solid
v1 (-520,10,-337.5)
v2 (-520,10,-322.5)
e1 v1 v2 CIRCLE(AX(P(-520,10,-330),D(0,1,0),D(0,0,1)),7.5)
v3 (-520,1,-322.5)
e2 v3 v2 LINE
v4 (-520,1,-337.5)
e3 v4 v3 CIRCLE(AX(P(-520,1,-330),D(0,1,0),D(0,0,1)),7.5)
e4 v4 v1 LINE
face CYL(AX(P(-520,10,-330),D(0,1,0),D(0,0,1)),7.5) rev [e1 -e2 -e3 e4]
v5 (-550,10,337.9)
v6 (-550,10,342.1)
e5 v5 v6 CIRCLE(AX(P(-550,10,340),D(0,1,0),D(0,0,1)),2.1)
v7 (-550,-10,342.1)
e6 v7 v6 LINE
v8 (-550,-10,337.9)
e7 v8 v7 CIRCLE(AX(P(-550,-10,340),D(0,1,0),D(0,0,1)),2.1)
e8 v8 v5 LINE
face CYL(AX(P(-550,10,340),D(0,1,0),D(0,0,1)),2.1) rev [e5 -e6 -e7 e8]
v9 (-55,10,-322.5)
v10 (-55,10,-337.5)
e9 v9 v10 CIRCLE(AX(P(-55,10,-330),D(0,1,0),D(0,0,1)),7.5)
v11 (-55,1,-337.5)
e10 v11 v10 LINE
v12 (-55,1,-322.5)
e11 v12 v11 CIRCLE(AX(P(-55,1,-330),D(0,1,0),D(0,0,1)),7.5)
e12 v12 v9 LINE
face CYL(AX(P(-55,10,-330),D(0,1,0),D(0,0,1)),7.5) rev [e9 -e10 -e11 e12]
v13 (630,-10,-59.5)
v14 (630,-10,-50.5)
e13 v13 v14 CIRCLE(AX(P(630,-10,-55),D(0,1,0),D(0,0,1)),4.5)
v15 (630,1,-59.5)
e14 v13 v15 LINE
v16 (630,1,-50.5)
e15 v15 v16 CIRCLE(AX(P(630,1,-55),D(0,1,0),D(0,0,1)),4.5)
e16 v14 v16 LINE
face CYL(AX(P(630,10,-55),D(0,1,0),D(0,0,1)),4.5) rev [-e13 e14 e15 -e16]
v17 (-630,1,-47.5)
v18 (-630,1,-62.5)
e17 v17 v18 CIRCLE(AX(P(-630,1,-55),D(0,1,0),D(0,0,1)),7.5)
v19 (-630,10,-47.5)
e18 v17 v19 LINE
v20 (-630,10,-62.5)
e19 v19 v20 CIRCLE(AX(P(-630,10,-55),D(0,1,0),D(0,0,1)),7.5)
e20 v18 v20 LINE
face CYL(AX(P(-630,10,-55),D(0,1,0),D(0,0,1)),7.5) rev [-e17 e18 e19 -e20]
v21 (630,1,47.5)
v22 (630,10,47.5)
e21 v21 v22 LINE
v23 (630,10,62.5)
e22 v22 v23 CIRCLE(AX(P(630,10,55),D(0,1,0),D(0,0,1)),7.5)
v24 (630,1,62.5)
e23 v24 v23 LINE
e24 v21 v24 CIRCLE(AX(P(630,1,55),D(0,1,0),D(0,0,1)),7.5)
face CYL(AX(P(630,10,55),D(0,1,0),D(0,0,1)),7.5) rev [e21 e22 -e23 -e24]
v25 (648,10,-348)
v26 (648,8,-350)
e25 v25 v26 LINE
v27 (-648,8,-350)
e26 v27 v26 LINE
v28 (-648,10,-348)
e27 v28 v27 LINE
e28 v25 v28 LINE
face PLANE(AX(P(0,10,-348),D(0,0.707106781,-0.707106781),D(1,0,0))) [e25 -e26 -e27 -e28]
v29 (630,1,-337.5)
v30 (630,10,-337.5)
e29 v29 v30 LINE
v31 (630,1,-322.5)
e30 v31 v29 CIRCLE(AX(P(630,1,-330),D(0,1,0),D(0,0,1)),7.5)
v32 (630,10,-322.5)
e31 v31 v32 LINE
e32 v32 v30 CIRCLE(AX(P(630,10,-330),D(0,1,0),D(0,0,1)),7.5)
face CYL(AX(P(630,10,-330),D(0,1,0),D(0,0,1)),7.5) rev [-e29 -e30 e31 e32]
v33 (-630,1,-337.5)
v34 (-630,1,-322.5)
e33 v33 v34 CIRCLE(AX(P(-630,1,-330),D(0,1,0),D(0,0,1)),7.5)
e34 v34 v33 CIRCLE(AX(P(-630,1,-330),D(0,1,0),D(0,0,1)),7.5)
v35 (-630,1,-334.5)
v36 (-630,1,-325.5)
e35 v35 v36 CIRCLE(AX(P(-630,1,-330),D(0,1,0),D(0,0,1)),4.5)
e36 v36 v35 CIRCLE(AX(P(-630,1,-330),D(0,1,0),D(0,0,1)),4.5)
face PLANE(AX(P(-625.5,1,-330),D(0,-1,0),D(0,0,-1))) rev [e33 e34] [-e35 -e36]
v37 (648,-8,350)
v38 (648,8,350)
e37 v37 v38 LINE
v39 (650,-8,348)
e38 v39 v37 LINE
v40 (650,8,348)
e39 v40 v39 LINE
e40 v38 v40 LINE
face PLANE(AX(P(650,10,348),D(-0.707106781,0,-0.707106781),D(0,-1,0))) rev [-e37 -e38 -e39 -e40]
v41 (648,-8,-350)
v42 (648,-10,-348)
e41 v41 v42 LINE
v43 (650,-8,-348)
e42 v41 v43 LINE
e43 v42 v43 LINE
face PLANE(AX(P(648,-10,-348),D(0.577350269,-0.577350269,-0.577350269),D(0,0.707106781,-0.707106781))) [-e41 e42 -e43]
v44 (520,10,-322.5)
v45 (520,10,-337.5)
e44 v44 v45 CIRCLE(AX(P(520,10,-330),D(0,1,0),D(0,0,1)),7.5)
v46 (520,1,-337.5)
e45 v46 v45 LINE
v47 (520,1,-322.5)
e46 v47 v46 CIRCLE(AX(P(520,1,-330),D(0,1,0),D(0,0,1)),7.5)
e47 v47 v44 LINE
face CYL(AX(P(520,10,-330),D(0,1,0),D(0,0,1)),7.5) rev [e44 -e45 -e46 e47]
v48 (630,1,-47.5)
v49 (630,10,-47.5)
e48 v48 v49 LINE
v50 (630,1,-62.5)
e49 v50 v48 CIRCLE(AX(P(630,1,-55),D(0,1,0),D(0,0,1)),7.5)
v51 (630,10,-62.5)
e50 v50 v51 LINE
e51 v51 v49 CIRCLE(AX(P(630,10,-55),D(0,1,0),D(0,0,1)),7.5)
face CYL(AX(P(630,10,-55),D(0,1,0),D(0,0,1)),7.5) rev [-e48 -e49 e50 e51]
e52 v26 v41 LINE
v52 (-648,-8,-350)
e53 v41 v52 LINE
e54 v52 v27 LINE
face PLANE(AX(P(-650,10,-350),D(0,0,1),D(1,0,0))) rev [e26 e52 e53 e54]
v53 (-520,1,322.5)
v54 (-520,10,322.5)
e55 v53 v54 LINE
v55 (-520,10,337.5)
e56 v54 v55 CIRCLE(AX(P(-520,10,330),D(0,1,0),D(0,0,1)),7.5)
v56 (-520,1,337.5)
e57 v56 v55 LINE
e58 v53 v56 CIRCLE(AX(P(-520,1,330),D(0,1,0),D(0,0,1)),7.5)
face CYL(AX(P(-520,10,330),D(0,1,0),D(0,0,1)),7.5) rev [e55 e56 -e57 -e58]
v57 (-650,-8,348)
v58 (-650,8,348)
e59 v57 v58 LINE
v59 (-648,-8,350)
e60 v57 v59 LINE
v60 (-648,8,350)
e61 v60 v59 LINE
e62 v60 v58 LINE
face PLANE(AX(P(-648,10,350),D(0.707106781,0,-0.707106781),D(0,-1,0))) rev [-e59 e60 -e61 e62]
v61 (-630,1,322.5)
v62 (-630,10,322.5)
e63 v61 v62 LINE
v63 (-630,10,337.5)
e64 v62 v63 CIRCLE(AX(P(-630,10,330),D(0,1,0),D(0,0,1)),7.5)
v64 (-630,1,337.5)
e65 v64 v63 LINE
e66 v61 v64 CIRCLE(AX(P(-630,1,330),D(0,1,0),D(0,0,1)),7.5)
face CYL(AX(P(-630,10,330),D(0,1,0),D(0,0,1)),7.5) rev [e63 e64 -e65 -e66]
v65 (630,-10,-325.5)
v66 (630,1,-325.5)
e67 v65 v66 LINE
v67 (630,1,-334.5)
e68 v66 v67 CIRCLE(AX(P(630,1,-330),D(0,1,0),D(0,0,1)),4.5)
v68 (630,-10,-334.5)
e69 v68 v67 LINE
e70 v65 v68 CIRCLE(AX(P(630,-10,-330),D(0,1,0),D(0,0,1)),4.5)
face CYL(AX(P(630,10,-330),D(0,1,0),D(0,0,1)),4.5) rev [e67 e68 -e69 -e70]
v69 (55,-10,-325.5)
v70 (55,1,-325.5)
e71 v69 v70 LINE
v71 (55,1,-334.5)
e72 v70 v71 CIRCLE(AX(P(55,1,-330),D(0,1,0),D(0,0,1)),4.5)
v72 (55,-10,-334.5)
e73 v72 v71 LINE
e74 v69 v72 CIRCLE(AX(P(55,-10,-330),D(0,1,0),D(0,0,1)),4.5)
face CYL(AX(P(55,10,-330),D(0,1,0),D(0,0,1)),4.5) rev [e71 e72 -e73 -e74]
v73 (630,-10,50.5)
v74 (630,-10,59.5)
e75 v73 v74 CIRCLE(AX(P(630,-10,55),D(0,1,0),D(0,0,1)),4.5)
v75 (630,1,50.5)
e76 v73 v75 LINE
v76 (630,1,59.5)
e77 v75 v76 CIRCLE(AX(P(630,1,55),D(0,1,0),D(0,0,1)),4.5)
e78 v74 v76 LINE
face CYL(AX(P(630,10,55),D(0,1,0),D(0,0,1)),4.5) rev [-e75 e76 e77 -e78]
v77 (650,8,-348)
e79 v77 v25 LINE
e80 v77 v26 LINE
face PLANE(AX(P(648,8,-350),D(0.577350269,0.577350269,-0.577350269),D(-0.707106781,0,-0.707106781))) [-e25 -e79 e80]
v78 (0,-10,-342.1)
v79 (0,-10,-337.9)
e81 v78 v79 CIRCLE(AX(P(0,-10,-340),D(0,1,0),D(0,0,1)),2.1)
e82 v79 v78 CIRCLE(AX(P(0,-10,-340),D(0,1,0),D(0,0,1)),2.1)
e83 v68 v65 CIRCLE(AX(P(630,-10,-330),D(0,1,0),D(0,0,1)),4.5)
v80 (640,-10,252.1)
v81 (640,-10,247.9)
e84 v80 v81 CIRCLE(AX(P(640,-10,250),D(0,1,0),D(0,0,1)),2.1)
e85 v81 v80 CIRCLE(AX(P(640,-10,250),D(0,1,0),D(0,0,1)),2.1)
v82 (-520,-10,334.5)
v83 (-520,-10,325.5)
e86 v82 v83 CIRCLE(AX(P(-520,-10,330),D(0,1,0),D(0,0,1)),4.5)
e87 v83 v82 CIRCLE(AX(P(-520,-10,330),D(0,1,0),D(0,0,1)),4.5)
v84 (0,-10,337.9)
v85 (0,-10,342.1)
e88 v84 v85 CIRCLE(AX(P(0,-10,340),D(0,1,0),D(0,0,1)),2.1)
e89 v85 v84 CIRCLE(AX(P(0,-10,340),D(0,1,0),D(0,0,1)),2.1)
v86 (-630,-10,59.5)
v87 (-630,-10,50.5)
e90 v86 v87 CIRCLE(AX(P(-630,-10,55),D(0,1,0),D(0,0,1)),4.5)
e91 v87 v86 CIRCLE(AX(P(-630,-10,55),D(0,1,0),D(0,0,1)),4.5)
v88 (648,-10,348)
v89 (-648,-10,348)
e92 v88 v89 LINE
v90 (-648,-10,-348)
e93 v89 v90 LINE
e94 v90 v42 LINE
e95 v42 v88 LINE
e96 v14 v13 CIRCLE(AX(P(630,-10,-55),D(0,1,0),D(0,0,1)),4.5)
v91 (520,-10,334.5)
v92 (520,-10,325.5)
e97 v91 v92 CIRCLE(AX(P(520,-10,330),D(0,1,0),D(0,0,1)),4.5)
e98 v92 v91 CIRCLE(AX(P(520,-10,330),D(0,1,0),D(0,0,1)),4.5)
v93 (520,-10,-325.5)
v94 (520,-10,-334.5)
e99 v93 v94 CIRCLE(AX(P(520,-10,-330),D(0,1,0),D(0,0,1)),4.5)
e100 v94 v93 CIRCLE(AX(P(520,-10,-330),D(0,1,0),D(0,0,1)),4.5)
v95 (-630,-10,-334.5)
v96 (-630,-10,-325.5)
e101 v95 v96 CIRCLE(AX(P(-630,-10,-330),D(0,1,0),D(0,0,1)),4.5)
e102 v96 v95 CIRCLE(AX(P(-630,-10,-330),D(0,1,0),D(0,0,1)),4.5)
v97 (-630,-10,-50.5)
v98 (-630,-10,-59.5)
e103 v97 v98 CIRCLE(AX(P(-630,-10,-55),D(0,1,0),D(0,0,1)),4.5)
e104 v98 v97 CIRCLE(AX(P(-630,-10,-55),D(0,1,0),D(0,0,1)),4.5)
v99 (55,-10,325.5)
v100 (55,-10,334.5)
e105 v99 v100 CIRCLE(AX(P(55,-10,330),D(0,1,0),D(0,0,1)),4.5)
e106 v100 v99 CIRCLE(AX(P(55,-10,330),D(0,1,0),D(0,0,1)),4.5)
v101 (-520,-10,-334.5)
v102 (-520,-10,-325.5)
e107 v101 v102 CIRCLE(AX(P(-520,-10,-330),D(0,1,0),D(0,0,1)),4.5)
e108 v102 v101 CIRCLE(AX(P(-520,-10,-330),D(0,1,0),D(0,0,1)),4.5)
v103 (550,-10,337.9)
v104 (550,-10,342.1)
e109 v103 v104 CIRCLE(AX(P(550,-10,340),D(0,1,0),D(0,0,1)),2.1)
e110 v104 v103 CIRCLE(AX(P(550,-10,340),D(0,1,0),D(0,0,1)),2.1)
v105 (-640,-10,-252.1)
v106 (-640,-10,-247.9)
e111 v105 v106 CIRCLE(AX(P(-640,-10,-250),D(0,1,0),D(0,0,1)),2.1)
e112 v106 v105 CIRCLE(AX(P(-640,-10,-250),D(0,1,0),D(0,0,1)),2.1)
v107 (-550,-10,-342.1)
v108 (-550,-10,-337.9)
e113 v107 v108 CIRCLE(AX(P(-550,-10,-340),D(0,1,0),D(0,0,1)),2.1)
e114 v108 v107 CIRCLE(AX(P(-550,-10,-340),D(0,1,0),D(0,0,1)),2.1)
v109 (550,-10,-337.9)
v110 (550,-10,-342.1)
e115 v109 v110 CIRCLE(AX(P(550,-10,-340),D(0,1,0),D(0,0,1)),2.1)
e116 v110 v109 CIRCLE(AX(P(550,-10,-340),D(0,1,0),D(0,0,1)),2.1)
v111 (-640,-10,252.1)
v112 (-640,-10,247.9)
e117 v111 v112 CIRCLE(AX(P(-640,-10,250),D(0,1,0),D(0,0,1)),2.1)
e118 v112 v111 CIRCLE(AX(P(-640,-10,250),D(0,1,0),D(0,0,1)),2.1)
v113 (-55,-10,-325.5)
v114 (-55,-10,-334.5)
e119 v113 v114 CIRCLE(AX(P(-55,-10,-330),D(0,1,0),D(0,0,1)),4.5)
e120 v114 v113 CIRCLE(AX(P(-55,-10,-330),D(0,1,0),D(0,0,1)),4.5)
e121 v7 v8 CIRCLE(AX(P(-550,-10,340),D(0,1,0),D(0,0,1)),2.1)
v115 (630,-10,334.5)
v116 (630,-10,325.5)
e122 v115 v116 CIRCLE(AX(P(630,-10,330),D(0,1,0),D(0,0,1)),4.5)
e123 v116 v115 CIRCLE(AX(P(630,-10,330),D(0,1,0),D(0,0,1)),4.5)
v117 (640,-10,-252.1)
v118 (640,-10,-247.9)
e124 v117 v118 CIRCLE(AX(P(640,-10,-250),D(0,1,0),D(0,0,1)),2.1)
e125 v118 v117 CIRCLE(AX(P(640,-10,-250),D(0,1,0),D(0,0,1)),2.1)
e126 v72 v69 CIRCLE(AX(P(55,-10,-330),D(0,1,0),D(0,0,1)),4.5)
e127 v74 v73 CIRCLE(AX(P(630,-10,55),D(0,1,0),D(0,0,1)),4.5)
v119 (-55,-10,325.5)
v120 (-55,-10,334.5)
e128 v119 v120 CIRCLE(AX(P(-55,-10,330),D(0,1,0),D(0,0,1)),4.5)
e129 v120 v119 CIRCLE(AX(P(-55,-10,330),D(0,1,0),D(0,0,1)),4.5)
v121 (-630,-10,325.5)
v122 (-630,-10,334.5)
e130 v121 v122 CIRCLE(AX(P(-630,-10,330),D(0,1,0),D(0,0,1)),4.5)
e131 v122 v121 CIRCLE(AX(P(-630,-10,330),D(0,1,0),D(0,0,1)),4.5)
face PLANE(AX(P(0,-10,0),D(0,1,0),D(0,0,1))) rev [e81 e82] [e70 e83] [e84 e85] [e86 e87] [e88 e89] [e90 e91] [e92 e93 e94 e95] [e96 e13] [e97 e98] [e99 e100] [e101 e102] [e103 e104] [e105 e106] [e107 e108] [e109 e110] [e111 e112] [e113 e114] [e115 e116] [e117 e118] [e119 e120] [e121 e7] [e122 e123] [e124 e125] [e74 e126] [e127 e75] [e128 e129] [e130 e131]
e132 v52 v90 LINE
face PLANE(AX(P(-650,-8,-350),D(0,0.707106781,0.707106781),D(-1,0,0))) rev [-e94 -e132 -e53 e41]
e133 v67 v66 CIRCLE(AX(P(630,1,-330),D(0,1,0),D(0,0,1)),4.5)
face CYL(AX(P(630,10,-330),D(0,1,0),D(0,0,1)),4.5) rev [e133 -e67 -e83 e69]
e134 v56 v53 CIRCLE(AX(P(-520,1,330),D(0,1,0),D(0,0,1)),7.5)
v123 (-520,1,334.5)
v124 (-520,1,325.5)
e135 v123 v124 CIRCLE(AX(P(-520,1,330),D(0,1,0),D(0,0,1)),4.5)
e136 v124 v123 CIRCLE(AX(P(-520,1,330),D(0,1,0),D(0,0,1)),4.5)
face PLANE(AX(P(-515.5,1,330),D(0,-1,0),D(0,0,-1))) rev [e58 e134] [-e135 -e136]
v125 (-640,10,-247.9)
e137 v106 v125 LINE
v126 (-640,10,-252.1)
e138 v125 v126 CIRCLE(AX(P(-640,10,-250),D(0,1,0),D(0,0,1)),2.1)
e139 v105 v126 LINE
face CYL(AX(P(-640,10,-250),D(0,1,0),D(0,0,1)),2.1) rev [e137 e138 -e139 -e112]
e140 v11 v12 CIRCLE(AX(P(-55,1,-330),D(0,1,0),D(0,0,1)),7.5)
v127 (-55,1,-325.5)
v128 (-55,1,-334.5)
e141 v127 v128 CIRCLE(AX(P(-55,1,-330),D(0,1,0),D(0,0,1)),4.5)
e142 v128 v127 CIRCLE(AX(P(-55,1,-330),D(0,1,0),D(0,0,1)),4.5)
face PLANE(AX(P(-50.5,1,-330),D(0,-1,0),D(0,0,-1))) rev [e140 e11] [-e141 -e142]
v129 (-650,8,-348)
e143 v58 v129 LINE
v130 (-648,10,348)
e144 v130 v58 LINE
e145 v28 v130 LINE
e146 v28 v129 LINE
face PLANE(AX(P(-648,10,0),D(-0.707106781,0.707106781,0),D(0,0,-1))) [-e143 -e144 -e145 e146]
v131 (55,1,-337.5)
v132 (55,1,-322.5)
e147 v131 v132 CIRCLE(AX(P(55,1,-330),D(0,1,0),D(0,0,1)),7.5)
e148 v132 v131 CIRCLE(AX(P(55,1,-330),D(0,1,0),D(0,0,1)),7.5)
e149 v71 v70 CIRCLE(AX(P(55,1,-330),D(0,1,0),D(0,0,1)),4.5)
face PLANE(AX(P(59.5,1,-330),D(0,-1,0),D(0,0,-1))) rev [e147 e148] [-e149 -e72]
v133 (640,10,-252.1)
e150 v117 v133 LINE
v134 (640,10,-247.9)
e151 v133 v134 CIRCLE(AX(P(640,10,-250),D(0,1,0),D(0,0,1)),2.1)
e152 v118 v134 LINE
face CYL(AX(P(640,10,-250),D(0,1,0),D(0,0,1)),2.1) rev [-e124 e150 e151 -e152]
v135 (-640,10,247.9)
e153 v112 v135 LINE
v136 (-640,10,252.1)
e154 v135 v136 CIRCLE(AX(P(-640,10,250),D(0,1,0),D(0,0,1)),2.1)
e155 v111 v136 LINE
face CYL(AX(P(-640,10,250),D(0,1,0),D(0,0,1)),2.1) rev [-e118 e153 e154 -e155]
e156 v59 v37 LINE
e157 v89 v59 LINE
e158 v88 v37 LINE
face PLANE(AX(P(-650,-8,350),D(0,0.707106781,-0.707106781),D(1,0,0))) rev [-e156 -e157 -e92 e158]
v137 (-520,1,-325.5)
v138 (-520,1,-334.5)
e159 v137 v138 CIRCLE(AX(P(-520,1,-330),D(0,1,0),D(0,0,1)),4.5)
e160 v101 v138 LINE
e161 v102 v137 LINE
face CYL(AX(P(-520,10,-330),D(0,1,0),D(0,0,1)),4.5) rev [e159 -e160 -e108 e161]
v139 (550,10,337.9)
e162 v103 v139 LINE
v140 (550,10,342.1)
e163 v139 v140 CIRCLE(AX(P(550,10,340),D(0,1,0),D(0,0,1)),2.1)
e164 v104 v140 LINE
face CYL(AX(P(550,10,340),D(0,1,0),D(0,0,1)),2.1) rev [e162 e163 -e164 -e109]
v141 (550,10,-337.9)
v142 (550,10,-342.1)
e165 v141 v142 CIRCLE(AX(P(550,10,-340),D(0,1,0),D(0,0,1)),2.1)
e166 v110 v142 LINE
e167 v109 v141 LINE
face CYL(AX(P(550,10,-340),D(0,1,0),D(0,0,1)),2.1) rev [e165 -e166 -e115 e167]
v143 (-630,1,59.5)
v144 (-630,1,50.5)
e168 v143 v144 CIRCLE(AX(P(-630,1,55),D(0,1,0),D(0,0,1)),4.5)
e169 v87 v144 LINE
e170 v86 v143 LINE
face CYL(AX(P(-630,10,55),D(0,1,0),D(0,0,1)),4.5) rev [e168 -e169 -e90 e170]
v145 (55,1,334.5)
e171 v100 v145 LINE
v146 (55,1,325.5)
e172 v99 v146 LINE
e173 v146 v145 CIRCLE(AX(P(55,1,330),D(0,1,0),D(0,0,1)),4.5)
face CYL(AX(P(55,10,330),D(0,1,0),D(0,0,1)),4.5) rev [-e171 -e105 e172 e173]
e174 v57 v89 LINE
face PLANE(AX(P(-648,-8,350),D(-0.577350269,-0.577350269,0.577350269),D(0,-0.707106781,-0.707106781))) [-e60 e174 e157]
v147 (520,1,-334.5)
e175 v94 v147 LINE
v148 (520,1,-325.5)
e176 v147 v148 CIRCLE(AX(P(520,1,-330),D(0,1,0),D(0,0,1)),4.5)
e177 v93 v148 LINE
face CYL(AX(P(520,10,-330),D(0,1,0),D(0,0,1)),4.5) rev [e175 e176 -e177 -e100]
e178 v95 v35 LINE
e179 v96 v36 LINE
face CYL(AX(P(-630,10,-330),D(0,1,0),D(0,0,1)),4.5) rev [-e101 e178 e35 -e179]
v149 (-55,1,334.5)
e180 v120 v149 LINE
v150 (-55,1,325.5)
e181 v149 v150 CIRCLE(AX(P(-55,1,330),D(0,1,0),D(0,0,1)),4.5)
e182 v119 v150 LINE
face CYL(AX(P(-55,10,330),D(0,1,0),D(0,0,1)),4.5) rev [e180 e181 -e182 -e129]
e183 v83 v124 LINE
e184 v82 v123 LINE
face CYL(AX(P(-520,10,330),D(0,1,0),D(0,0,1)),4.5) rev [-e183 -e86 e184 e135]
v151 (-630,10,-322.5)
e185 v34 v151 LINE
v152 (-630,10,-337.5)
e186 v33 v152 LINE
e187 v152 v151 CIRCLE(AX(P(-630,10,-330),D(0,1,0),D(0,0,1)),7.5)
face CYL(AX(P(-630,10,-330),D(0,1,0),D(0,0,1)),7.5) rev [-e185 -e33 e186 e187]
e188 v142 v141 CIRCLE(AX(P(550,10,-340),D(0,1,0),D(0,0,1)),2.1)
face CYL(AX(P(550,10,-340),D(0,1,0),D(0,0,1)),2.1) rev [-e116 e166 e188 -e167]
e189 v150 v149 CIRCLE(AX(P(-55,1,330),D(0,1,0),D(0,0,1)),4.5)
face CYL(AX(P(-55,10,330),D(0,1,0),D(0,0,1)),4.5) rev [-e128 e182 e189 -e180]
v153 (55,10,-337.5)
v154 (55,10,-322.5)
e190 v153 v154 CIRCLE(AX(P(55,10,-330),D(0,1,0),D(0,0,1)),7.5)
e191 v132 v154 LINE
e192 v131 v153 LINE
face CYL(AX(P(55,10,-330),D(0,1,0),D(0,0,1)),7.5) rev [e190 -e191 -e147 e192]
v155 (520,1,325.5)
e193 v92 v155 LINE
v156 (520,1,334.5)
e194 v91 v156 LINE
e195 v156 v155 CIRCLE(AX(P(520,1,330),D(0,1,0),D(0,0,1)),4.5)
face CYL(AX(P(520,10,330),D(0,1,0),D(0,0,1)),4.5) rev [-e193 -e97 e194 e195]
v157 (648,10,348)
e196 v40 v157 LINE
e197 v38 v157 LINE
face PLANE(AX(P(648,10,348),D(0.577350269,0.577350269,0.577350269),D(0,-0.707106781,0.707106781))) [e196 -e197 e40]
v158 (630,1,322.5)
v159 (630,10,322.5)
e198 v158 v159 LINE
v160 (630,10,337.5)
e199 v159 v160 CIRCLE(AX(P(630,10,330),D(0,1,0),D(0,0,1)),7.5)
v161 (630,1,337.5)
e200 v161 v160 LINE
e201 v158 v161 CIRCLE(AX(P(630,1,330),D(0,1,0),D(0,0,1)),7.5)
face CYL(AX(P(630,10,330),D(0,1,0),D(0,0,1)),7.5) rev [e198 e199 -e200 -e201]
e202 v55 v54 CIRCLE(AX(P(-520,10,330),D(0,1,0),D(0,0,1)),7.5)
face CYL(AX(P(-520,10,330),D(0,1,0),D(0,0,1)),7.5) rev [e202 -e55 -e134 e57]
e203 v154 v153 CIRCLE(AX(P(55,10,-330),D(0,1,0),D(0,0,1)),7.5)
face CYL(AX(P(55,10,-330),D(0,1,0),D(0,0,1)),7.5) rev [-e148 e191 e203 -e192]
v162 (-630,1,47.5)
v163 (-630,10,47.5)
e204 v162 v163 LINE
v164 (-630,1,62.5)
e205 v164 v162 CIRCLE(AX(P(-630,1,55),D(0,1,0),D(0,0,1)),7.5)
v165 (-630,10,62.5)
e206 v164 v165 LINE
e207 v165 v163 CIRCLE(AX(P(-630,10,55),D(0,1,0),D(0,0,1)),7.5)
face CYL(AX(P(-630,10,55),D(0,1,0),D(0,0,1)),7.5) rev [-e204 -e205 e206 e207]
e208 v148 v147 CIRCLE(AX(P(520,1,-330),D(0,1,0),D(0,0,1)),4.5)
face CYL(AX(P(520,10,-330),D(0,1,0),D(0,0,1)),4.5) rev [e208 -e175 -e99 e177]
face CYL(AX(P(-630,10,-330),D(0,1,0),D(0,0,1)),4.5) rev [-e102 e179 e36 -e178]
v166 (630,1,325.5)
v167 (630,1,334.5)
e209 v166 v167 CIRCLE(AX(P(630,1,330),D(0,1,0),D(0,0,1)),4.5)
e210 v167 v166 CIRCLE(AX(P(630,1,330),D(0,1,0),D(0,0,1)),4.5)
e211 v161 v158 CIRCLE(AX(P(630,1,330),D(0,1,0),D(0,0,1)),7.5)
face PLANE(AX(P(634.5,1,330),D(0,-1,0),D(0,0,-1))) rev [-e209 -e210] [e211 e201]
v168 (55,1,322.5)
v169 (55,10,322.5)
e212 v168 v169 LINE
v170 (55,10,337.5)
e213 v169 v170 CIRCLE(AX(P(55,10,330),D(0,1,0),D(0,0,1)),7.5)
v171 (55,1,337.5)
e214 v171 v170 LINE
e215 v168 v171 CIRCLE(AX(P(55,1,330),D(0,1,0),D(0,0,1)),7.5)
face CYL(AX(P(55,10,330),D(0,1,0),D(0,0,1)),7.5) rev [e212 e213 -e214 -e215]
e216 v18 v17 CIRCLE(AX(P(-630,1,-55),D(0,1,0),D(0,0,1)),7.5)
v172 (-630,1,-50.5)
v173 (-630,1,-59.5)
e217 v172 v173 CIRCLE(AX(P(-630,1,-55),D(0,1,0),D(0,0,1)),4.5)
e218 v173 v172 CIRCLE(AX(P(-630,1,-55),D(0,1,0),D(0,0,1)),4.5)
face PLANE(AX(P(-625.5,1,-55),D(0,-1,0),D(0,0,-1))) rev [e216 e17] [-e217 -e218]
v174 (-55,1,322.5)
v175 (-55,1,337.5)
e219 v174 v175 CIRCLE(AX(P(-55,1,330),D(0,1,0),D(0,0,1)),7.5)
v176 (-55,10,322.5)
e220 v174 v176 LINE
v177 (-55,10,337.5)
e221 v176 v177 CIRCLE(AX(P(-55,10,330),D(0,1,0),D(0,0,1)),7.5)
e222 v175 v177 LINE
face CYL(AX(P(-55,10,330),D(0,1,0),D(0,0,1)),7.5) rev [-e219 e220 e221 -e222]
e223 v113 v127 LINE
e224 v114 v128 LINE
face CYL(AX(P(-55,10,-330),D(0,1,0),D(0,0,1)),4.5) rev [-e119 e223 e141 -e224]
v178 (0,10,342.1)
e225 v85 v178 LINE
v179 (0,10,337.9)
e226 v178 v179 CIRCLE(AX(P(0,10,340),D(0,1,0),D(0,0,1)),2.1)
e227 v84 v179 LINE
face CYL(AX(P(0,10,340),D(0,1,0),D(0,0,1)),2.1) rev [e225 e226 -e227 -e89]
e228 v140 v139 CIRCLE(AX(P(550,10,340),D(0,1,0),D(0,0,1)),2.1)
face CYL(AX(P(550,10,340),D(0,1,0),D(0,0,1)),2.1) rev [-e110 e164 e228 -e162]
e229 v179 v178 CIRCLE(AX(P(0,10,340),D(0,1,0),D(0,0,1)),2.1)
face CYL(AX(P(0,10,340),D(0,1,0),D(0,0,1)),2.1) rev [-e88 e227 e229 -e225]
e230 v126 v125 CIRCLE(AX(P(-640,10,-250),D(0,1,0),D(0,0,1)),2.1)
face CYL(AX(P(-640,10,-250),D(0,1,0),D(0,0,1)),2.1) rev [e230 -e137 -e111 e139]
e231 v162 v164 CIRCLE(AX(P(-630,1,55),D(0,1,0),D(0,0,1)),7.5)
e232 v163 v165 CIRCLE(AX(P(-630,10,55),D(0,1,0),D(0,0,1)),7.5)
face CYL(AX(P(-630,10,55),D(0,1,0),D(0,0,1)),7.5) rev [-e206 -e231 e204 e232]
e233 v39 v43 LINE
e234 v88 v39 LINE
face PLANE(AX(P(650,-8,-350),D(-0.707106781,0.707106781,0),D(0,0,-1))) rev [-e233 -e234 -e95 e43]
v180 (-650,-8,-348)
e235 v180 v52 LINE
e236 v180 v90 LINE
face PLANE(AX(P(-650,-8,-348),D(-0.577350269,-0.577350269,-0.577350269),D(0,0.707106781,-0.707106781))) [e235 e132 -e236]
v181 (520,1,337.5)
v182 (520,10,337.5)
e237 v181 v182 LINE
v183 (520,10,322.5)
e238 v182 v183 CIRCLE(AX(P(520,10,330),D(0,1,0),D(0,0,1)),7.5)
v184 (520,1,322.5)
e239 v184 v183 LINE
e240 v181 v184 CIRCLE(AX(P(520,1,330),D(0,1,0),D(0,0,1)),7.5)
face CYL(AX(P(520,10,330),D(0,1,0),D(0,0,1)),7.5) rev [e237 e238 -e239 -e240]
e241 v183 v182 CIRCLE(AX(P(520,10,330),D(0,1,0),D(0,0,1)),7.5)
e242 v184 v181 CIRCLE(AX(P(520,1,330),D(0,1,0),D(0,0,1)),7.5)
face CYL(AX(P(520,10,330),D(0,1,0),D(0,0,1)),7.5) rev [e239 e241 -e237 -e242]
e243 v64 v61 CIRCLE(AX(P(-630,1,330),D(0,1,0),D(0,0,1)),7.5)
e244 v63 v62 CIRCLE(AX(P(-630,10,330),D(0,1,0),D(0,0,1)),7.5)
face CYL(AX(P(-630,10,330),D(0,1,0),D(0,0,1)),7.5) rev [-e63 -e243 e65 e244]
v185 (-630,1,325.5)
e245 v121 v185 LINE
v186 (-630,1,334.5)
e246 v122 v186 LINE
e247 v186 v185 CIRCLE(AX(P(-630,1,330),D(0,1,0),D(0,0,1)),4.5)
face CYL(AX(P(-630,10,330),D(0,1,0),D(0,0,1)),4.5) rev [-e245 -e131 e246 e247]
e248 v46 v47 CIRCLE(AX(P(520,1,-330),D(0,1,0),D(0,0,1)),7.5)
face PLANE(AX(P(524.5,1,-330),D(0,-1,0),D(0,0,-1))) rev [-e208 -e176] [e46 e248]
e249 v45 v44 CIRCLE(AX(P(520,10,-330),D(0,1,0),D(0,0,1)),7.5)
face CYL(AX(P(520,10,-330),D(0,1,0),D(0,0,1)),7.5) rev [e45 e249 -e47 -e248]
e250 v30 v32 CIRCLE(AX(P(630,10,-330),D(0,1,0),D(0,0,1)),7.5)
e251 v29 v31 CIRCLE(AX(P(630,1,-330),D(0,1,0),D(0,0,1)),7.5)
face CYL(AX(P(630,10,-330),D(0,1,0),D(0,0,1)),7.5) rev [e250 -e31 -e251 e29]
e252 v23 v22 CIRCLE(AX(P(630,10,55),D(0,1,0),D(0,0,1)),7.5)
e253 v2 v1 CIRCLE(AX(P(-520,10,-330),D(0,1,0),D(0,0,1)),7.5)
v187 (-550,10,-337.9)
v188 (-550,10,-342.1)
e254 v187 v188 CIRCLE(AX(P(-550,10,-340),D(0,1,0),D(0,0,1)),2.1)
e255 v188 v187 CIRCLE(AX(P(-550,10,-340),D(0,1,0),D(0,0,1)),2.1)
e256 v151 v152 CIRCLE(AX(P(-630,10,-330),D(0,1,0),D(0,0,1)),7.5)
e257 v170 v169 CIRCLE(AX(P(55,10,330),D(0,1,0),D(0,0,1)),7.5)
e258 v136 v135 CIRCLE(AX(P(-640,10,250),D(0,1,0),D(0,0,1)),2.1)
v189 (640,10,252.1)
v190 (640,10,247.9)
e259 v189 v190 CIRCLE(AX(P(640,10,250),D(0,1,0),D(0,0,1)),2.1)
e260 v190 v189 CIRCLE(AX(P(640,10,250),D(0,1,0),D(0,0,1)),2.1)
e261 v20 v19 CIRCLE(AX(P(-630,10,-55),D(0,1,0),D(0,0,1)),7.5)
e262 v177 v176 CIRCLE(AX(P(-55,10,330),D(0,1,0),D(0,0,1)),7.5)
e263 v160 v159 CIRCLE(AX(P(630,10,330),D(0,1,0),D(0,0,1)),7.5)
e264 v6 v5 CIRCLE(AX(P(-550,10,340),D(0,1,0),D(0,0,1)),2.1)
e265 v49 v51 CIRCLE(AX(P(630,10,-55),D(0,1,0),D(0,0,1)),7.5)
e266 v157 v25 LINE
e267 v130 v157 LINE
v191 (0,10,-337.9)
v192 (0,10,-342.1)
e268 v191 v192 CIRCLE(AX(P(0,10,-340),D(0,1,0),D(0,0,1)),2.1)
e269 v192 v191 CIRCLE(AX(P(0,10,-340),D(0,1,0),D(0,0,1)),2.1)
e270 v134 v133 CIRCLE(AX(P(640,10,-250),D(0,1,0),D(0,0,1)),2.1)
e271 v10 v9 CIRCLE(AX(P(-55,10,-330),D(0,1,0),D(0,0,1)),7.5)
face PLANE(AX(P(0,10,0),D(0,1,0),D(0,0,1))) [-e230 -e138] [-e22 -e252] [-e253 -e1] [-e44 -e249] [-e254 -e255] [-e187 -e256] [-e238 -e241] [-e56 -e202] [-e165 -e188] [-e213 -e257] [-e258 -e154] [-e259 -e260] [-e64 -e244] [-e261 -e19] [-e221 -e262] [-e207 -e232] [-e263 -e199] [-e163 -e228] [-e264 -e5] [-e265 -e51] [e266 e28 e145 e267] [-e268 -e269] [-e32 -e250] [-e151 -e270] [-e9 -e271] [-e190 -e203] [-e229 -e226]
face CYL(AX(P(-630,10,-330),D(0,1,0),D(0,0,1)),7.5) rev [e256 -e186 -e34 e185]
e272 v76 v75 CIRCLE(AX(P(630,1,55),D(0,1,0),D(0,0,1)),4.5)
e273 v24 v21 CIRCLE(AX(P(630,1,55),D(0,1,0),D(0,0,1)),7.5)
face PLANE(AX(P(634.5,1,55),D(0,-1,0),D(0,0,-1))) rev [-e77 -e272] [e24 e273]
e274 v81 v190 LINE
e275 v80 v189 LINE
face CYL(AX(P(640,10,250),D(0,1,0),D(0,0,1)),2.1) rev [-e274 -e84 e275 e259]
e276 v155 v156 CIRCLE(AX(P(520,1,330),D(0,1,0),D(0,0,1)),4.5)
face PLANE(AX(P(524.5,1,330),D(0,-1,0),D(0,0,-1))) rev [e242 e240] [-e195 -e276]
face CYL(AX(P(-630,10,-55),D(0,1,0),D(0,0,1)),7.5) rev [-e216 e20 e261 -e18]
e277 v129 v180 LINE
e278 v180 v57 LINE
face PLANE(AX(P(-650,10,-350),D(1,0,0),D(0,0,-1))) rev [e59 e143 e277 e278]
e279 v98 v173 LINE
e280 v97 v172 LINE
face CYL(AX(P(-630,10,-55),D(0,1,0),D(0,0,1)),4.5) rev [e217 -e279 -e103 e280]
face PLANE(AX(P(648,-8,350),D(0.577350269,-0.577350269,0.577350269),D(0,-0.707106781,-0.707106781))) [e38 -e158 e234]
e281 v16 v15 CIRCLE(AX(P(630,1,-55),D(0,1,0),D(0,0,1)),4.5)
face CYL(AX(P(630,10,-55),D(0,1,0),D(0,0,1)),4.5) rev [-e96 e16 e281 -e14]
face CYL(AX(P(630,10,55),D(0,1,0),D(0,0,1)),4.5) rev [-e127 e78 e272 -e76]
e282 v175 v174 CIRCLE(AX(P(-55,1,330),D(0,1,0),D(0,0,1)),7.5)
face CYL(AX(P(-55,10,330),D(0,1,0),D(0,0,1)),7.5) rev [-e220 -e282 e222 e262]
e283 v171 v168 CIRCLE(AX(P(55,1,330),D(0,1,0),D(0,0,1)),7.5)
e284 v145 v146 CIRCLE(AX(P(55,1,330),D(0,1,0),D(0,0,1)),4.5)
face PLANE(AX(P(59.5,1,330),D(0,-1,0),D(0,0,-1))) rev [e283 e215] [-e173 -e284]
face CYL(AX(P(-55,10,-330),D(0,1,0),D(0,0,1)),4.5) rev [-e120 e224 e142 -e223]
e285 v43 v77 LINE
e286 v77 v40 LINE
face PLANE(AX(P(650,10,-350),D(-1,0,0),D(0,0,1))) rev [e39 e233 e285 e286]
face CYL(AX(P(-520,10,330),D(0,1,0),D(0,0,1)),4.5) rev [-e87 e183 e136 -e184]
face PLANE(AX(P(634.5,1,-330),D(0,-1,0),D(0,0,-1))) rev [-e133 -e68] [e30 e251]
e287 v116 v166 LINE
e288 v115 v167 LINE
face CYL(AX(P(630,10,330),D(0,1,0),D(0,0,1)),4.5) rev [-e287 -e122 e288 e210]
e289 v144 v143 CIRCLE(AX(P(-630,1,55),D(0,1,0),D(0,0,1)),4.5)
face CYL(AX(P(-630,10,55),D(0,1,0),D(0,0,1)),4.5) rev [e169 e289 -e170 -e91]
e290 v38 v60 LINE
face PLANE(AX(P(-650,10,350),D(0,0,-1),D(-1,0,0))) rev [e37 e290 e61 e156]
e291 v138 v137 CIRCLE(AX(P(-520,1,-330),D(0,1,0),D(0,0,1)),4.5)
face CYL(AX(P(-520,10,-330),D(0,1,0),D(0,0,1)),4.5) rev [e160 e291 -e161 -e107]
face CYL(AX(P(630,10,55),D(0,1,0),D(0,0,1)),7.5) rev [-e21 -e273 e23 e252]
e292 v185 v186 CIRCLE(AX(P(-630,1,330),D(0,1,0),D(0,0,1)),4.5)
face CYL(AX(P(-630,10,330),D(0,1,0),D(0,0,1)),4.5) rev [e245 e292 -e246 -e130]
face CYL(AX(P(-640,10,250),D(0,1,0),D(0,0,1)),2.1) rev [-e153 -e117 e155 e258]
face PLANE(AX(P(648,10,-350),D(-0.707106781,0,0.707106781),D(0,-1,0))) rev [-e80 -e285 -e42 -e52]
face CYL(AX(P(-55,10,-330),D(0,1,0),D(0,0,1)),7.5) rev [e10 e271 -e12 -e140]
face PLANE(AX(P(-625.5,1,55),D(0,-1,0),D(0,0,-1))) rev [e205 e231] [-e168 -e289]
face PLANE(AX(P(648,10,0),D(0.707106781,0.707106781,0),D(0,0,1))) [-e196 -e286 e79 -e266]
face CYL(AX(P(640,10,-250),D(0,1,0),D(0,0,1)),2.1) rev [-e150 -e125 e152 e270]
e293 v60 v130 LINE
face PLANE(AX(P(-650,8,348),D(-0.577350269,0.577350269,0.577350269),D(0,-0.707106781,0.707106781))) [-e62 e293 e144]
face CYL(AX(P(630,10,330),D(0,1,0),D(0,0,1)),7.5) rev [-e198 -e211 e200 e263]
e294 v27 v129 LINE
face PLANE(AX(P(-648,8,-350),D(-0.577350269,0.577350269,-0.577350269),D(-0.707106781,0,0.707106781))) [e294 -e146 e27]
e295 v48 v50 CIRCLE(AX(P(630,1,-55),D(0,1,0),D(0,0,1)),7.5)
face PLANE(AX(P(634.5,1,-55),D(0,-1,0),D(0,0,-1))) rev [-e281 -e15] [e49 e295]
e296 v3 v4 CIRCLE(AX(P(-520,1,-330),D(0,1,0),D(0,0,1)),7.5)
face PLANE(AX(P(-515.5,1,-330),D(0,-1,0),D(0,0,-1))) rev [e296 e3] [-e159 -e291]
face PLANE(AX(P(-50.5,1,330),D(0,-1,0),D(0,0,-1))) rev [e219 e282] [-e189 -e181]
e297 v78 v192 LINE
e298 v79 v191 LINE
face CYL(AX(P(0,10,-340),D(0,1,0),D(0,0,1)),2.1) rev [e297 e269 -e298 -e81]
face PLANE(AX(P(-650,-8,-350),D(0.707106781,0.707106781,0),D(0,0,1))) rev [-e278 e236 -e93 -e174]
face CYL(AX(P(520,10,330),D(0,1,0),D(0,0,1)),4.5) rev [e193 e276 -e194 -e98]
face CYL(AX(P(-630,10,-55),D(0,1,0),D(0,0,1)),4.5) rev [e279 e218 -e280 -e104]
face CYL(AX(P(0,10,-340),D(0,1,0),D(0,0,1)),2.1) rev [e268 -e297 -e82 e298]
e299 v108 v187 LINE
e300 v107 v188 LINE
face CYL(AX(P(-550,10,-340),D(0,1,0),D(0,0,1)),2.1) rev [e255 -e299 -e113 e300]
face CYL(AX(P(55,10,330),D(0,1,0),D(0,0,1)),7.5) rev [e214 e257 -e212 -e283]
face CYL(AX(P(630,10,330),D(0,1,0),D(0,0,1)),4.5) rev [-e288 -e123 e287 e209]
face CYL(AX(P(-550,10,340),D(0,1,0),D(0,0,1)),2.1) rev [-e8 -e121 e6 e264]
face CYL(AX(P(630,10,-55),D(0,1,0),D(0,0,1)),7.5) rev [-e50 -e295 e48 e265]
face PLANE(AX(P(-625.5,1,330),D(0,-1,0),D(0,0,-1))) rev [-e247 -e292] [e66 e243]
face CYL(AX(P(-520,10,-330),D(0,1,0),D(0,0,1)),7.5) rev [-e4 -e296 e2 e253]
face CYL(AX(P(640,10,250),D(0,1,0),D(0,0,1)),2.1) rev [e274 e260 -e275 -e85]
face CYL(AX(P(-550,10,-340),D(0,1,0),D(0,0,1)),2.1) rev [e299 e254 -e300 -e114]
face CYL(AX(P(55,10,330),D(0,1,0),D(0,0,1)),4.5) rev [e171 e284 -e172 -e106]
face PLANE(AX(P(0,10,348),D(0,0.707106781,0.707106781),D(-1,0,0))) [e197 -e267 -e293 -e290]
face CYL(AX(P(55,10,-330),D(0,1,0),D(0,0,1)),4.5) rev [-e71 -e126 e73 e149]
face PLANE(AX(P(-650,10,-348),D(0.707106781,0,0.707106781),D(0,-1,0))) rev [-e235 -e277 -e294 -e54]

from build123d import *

# Parameters (mm, degrees)
SKETCH_1_W                          = 1300
SKETCH_1_H                          = 700
EXTRUDE_1_DEPTH                     = 10
CHAMFER_1_SIZE                      = 2
HOLE_WIZARD_1_D                     = 9
HOLE_WIZARD_1_CBORE_D               = 15
HOLE_WIZARD_1_CBORE_DEPTH           = 9
PATTERN_LINEAR_1_COUNT              = 2
PATTERN_LINEAR_1_PITCH              = 110
HOLE_WIZARD_2_D                     = 9
HOLE_WIZARD_2_CBORE_D               = 15
HOLE_WIZARD_2_CBORE_DEPTH           = 9
PATTERN_LINEAR_2_COUNT              = 2
PATTERN_LINEAR_2_PITCH              = 110
MIRROR_1_COPY_1_D                   = 9
MIRROR_1_COPY_1_CBORE_D             = 15
MIRROR_1_COPY_1_CBORE_DEPTH         = 9
MIRROR_2_COPY_1_D                   = 9
MIRROR_2_COPY_1_CBORE_D             = 15
MIRROR_2_COPY_1_CBORE_DEPTH         = 9
PATTERN_LINEAR_3_COUNT              = 3
PATTERN_LINEAR_3_PITCH              = 575
PATTERN_LINEAR_3_COPY_1_D           = 9
PATTERN_LINEAR_3_COPY_1_CBORE_D     = 15
PATTERN_LINEAR_3_COPY_1_CBORE_DEPTH = 9
PATTERN_LINEAR_3_COPY_2_D           = 9
PATTERN_LINEAR_3_COPY_2_CBORE_D     = 15
PATTERN_LINEAR_3_COPY_2_CBORE_DEPTH = 9
PATTERN_LINEAR_3_COPY_3_D           = 9
PATTERN_LINEAR_3_COPY_3_CBORE_D     = 15
PATTERN_LINEAR_3_COPY_3_CBORE_DEPTH = 9
PATTERN_LINEAR_3_COPY_4_D           = 9
PATTERN_LINEAR_3_COPY_4_CBORE_D     = 15
PATTERN_LINEAR_3_COPY_4_CBORE_DEPTH = 9
PATTERN_LINEAR_3_COPY_5_D           = 9
PATTERN_LINEAR_3_COPY_5_CBORE_D     = 15
PATTERN_LINEAR_3_COPY_5_CBORE_DEPTH = 9
PATTERN_LINEAR_3_COPY_6_D           = 9
PATTERN_LINEAR_3_COPY_6_CBORE_D     = 15
PATTERN_LINEAR_3_COPY_6_CBORE_DEPTH = 9
PATTERN_LINEAR_4_COUNT              = 3
PATTERN_LINEAR_4_PITCH              = 550


with BuildPart() as part:
    # 草图1 → 凸台-拉伸1 (new, symmetric)
    with BuildSketch(Plane(origin=(0, 0, 0), x_dir=(1, 0, 0), z_dir=(0, 1, 0))):
        Rectangle(SKETCH_1_W, SKETCH_1_H)
    extrude(amount=EXTRUDE_1_DEPTH, both=True)

    # 倒角1
    chamfer_1_edges = [part.edges().sort_by_distance(p)[0] for p in [
        (650, 10, 0),
        (0, 10, -350),
        (-650, 10, 0),
        (0, -10, -350),
        (650, -10, 0),
        (0, -10, 350),
        (-650, -10, 0),
        (0, 10, 350),
        (-650, 0, -350),
        (650, 0, -350),
        (650, 0, 350),
        (-650, 0, 350),
    ]]
    chamfer(chamfer_1_edges, length=CHAMFER_1_SIZE)

    # 打孔尺寸根据内六角圆柱头螺钉的类型1 (through all)
    with Locations(Plane(origin=(630, 10, -330), x_dir=(0, 0, 1), z_dir=(0, 1, 0))):
        with Locations((0, 0)):
            hole_wizard_1 = CounterBoreHole(HOLE_WIZARD_1_D / 2, HOLE_WIZARD_1_CBORE_D / 2, HOLE_WIZARD_1_CBORE_DEPTH)

    # 阵列(线性)1: 打孔尺寸根据内六角圆柱头螺钉的类型1 ×2
    with Locations(*[(-i * PATTERN_LINEAR_1_PITCH, 0, 0) for i in range(1, PATTERN_LINEAR_1_COUNT)]):
        add(hole_wizard_1, mode=Mode.SUBTRACT)

    # 打孔尺寸根据内六角圆柱头螺钉的类型2 (through all)
    with Locations(Plane(origin=(630, 10, -55), x_dir=(0, 0, 1), z_dir=(0, 1, 0))):
        with Locations((0, 0)):
            hole_wizard_2 = CounterBoreHole(HOLE_WIZARD_2_D / 2, HOLE_WIZARD_2_CBORE_D / 2, HOLE_WIZARD_2_CBORE_DEPTH)

    # 阵列(线性)2: 打孔尺寸根据内六角圆柱头螺钉的类型2 ×2
    with Locations(*[(0, 0, i * PATTERN_LINEAR_2_PITCH) for i in range(1, PATTERN_LINEAR_2_COUNT)]):
        add(hole_wizard_2, mode=Mode.SUBTRACT)

    # 镜向1: 打孔尺寸根据内六角圆柱头螺钉的类型2 across plane
    add(hole_wizard_2.mirror(Plane(origin=(0, 0, 0), x_dir=(0, 0, 1), z_dir=(1, 0, 0))), mode=Mode.SUBTRACT)

    # 镜向1 copy 1 (through all)
    with Locations(Plane(origin=(-630, 10, 55), x_dir=(0, 0, 1), z_dir=(0, 1, 0))):
        with Locations((0, 0)):
            CounterBoreHole(MIRROR_1_COPY_1_D / 2, MIRROR_1_COPY_1_CBORE_D / 2, MIRROR_1_COPY_1_CBORE_DEPTH)

    # 镜向2: 打孔尺寸根据内六角圆柱头螺钉的类型1 across plane
    add(hole_wizard_1.mirror(Plane.XY), mode=Mode.SUBTRACT)

    # 镜向2 copy 1 (through all)
    with Locations(Plane(origin=(520, 10, 330), x_dir=(0, 0, -1), z_dir=(0, 1, 0))):
        with Locations((0, 0)):
            CounterBoreHole(MIRROR_2_COPY_1_D / 2, MIRROR_2_COPY_1_CBORE_D / 2, MIRROR_2_COPY_1_CBORE_DEPTH)

    # 阵列(线性)3: 打孔尺寸根据内六角圆柱头螺钉的类型1 ×3
    with Locations(*[(-i * PATTERN_LINEAR_3_PITCH, 0, 0) for i in range(1, PATTERN_LINEAR_3_COUNT)]):
        add(hole_wizard_1, mode=Mode.SUBTRACT)

    # 阵列(线性)3 copy 1 (through all)
    with Locations(Plane(origin=(-55, 10, -330), x_dir=(0, 0, 1), z_dir=(0, 1, 0))):
        with Locations((0, 0)):
            CounterBoreHole(PATTERN_LINEAR_3_COPY_1_D / 2, PATTERN_LINEAR_3_COPY_1_CBORE_D / 2, PATTERN_LINEAR_3_COPY_1_CBORE_DEPTH)

    # 阵列(线性)3 copy 2 (through all)
    with Locations(Plane(origin=(-630, 10, -330), x_dir=(0, 0, 1), z_dir=(0, 1, 0))):
        with Locations((0, 0)):
            CounterBoreHole(PATTERN_LINEAR_3_COPY_2_D / 2, PATTERN_LINEAR_3_COPY_2_CBORE_D / 2, PATTERN_LINEAR_3_COPY_2_CBORE_DEPTH)

    # 阵列(线性)3 copy 3 (through all)
    with Locations(Plane(origin=(55, 10, 330), x_dir=(0, 0, -1), z_dir=(0, 1, 0))):
        with Locations((0, 0)):
            CounterBoreHole(PATTERN_LINEAR_3_COPY_3_D / 2, PATTERN_LINEAR_3_COPY_3_CBORE_D / 2, PATTERN_LINEAR_3_COPY_3_CBORE_DEPTH)

    # 阵列(线性)3 copy 4 (through all)
    with Locations(Plane(origin=(-520, 10, 330), x_dir=(0, 0, -1), z_dir=(0, 1, 0))):
        with Locations((0, 0)):
            CounterBoreHole(PATTERN_LINEAR_3_COPY_4_D / 2, PATTERN_LINEAR_3_COPY_4_CBORE_D / 2, PATTERN_LINEAR_3_COPY_4_CBORE_DEPTH)

    # 阵列(线性)3 copy 5 (through all)
    with Locations(Plane(origin=(-55, 10, 330), x_dir=(0, 0, -1), z_dir=(0, 1, 0))):
        with Locations((0, 0)):
            CounterBoreHole(PATTERN_LINEAR_3_COPY_5_D / 2, PATTERN_LINEAR_3_COPY_5_CBORE_D / 2, PATTERN_LINEAR_3_COPY_5_CBORE_DEPTH)

    # 阵列(线性)3 copy 6 (through all)
    with Locations(Plane(origin=(-630, 10, 330), x_dir=(0, 0, -1), z_dir=(0, 1, 0))):
        with Locations((0, 0)):
            CounterBoreHole(PATTERN_LINEAR_3_COPY_6_D / 2, PATTERN_LINEAR_3_COPY_6_CBORE_D / 2, PATTERN_LINEAR_3_COPY_6_CBORE_DEPTH)

    # 草图14 → M5 螺纹孔1 (revolve, cut)
    with BuildSketch(Plane(origin=(550, 10, -340), x_dir=(0, 0, 1), z_dir=(1, 0, 0))):
        Polygon((0, 0), (0, 23.6618073), (2.1, 22.4), (2.1, 0), align=None)
    hole_wizard_m5_1 = revolve(axis=Axis((550, 16.35, -340), (0, -1, 0)), mode=Mode.SUBTRACT)

    # 阵列(线性)4: M5 螺纹孔1 ×3
    with Locations(*[(-i * PATTERN_LINEAR_4_PITCH, 0, 0) for i in range(1, PATTERN_LINEAR_4_COUNT)]):
        add(hole_wizard_m5_1, mode=Mode.SUBTRACT)

    # 镜向3: M5 螺纹孔1 across plane
    add(hole_wizard_m5_1.mirror(Plane.XY), mode=Mode.SUBTRACT)

    # 镜向3 copy 1 sketch → 镜向3 copy 1 (revolve, cut)
    with BuildSketch(Plane(origin=(0, 10, 340), x_dir=(0, 0, -1), z_dir=(1, 0, 0))):
        Polygon((0, 0), (0, -23.6618073), (2.1, -22.4), (2.1, 0), align=None)
    revolve(axis=Axis((0, 16.35, 340), (0, 1, 0)), mode=Mode.SUBTRACT)

    # 镜向3 copy 2 sketch → 镜向3 copy 2 (revolve, cut)
    with BuildSketch(Plane(origin=(-550, 10, 340), x_dir=(0, 0, -1), z_dir=(1, 0, 0))):
        Polygon((0, 0), (0, -23.6618073), (2.1, -22.4), (2.1, 0), align=None)
    revolve(axis=Axis((-550, 16.35, 340), (0, 1, 0)), mode=Mode.SUBTRACT)

    # 草图15 → M5 螺纹孔2 (revolve, cut)
    with BuildSketch(Plane(origin=(-640, 10, -250), x_dir=(0, 0, 1), z_dir=(1, 0, 0))):
        Polygon((0, 0), (0, 23.6618073), (2.1, 22.4), (2.1, 0), align=None)
    hole_wizard_m5_2 = revolve(axis=Axis((-640, 16.35, -250), (0, -1, 0)), mode=Mode.SUBTRACT)

    # 镜向4: M5 螺纹孔2 across plane
    add(hole_wizard_m5_2.mirror(Plane.XY), mode=Mode.SUBTRACT)

    # 镜向5: M5 螺纹孔2 across plane
    add(hole_wizard_m5_2.mirror(Plane(origin=(0, 0, 0), x_dir=(0, 0, 1), z_dir=(1, 0, 0))), mode=Mode.SUBTRACT)

    # 镜向5 copy 1 sketch → 镜向5 copy 1 (revolve, cut)
    with BuildSketch(Plane(origin=(640, 10, 250), x_dir=(0, 0, -1), z_dir=(-1, 0, 0))):
        Polygon((0, 0), (0, 23.6618073), (2.1, 22.4), (2.1, 0), align=None)
    revolve(axis=Axis((640, 16.35, 250), (0, -1, 0)), mode=Mode.SUBTRACT)


solid = part.part
